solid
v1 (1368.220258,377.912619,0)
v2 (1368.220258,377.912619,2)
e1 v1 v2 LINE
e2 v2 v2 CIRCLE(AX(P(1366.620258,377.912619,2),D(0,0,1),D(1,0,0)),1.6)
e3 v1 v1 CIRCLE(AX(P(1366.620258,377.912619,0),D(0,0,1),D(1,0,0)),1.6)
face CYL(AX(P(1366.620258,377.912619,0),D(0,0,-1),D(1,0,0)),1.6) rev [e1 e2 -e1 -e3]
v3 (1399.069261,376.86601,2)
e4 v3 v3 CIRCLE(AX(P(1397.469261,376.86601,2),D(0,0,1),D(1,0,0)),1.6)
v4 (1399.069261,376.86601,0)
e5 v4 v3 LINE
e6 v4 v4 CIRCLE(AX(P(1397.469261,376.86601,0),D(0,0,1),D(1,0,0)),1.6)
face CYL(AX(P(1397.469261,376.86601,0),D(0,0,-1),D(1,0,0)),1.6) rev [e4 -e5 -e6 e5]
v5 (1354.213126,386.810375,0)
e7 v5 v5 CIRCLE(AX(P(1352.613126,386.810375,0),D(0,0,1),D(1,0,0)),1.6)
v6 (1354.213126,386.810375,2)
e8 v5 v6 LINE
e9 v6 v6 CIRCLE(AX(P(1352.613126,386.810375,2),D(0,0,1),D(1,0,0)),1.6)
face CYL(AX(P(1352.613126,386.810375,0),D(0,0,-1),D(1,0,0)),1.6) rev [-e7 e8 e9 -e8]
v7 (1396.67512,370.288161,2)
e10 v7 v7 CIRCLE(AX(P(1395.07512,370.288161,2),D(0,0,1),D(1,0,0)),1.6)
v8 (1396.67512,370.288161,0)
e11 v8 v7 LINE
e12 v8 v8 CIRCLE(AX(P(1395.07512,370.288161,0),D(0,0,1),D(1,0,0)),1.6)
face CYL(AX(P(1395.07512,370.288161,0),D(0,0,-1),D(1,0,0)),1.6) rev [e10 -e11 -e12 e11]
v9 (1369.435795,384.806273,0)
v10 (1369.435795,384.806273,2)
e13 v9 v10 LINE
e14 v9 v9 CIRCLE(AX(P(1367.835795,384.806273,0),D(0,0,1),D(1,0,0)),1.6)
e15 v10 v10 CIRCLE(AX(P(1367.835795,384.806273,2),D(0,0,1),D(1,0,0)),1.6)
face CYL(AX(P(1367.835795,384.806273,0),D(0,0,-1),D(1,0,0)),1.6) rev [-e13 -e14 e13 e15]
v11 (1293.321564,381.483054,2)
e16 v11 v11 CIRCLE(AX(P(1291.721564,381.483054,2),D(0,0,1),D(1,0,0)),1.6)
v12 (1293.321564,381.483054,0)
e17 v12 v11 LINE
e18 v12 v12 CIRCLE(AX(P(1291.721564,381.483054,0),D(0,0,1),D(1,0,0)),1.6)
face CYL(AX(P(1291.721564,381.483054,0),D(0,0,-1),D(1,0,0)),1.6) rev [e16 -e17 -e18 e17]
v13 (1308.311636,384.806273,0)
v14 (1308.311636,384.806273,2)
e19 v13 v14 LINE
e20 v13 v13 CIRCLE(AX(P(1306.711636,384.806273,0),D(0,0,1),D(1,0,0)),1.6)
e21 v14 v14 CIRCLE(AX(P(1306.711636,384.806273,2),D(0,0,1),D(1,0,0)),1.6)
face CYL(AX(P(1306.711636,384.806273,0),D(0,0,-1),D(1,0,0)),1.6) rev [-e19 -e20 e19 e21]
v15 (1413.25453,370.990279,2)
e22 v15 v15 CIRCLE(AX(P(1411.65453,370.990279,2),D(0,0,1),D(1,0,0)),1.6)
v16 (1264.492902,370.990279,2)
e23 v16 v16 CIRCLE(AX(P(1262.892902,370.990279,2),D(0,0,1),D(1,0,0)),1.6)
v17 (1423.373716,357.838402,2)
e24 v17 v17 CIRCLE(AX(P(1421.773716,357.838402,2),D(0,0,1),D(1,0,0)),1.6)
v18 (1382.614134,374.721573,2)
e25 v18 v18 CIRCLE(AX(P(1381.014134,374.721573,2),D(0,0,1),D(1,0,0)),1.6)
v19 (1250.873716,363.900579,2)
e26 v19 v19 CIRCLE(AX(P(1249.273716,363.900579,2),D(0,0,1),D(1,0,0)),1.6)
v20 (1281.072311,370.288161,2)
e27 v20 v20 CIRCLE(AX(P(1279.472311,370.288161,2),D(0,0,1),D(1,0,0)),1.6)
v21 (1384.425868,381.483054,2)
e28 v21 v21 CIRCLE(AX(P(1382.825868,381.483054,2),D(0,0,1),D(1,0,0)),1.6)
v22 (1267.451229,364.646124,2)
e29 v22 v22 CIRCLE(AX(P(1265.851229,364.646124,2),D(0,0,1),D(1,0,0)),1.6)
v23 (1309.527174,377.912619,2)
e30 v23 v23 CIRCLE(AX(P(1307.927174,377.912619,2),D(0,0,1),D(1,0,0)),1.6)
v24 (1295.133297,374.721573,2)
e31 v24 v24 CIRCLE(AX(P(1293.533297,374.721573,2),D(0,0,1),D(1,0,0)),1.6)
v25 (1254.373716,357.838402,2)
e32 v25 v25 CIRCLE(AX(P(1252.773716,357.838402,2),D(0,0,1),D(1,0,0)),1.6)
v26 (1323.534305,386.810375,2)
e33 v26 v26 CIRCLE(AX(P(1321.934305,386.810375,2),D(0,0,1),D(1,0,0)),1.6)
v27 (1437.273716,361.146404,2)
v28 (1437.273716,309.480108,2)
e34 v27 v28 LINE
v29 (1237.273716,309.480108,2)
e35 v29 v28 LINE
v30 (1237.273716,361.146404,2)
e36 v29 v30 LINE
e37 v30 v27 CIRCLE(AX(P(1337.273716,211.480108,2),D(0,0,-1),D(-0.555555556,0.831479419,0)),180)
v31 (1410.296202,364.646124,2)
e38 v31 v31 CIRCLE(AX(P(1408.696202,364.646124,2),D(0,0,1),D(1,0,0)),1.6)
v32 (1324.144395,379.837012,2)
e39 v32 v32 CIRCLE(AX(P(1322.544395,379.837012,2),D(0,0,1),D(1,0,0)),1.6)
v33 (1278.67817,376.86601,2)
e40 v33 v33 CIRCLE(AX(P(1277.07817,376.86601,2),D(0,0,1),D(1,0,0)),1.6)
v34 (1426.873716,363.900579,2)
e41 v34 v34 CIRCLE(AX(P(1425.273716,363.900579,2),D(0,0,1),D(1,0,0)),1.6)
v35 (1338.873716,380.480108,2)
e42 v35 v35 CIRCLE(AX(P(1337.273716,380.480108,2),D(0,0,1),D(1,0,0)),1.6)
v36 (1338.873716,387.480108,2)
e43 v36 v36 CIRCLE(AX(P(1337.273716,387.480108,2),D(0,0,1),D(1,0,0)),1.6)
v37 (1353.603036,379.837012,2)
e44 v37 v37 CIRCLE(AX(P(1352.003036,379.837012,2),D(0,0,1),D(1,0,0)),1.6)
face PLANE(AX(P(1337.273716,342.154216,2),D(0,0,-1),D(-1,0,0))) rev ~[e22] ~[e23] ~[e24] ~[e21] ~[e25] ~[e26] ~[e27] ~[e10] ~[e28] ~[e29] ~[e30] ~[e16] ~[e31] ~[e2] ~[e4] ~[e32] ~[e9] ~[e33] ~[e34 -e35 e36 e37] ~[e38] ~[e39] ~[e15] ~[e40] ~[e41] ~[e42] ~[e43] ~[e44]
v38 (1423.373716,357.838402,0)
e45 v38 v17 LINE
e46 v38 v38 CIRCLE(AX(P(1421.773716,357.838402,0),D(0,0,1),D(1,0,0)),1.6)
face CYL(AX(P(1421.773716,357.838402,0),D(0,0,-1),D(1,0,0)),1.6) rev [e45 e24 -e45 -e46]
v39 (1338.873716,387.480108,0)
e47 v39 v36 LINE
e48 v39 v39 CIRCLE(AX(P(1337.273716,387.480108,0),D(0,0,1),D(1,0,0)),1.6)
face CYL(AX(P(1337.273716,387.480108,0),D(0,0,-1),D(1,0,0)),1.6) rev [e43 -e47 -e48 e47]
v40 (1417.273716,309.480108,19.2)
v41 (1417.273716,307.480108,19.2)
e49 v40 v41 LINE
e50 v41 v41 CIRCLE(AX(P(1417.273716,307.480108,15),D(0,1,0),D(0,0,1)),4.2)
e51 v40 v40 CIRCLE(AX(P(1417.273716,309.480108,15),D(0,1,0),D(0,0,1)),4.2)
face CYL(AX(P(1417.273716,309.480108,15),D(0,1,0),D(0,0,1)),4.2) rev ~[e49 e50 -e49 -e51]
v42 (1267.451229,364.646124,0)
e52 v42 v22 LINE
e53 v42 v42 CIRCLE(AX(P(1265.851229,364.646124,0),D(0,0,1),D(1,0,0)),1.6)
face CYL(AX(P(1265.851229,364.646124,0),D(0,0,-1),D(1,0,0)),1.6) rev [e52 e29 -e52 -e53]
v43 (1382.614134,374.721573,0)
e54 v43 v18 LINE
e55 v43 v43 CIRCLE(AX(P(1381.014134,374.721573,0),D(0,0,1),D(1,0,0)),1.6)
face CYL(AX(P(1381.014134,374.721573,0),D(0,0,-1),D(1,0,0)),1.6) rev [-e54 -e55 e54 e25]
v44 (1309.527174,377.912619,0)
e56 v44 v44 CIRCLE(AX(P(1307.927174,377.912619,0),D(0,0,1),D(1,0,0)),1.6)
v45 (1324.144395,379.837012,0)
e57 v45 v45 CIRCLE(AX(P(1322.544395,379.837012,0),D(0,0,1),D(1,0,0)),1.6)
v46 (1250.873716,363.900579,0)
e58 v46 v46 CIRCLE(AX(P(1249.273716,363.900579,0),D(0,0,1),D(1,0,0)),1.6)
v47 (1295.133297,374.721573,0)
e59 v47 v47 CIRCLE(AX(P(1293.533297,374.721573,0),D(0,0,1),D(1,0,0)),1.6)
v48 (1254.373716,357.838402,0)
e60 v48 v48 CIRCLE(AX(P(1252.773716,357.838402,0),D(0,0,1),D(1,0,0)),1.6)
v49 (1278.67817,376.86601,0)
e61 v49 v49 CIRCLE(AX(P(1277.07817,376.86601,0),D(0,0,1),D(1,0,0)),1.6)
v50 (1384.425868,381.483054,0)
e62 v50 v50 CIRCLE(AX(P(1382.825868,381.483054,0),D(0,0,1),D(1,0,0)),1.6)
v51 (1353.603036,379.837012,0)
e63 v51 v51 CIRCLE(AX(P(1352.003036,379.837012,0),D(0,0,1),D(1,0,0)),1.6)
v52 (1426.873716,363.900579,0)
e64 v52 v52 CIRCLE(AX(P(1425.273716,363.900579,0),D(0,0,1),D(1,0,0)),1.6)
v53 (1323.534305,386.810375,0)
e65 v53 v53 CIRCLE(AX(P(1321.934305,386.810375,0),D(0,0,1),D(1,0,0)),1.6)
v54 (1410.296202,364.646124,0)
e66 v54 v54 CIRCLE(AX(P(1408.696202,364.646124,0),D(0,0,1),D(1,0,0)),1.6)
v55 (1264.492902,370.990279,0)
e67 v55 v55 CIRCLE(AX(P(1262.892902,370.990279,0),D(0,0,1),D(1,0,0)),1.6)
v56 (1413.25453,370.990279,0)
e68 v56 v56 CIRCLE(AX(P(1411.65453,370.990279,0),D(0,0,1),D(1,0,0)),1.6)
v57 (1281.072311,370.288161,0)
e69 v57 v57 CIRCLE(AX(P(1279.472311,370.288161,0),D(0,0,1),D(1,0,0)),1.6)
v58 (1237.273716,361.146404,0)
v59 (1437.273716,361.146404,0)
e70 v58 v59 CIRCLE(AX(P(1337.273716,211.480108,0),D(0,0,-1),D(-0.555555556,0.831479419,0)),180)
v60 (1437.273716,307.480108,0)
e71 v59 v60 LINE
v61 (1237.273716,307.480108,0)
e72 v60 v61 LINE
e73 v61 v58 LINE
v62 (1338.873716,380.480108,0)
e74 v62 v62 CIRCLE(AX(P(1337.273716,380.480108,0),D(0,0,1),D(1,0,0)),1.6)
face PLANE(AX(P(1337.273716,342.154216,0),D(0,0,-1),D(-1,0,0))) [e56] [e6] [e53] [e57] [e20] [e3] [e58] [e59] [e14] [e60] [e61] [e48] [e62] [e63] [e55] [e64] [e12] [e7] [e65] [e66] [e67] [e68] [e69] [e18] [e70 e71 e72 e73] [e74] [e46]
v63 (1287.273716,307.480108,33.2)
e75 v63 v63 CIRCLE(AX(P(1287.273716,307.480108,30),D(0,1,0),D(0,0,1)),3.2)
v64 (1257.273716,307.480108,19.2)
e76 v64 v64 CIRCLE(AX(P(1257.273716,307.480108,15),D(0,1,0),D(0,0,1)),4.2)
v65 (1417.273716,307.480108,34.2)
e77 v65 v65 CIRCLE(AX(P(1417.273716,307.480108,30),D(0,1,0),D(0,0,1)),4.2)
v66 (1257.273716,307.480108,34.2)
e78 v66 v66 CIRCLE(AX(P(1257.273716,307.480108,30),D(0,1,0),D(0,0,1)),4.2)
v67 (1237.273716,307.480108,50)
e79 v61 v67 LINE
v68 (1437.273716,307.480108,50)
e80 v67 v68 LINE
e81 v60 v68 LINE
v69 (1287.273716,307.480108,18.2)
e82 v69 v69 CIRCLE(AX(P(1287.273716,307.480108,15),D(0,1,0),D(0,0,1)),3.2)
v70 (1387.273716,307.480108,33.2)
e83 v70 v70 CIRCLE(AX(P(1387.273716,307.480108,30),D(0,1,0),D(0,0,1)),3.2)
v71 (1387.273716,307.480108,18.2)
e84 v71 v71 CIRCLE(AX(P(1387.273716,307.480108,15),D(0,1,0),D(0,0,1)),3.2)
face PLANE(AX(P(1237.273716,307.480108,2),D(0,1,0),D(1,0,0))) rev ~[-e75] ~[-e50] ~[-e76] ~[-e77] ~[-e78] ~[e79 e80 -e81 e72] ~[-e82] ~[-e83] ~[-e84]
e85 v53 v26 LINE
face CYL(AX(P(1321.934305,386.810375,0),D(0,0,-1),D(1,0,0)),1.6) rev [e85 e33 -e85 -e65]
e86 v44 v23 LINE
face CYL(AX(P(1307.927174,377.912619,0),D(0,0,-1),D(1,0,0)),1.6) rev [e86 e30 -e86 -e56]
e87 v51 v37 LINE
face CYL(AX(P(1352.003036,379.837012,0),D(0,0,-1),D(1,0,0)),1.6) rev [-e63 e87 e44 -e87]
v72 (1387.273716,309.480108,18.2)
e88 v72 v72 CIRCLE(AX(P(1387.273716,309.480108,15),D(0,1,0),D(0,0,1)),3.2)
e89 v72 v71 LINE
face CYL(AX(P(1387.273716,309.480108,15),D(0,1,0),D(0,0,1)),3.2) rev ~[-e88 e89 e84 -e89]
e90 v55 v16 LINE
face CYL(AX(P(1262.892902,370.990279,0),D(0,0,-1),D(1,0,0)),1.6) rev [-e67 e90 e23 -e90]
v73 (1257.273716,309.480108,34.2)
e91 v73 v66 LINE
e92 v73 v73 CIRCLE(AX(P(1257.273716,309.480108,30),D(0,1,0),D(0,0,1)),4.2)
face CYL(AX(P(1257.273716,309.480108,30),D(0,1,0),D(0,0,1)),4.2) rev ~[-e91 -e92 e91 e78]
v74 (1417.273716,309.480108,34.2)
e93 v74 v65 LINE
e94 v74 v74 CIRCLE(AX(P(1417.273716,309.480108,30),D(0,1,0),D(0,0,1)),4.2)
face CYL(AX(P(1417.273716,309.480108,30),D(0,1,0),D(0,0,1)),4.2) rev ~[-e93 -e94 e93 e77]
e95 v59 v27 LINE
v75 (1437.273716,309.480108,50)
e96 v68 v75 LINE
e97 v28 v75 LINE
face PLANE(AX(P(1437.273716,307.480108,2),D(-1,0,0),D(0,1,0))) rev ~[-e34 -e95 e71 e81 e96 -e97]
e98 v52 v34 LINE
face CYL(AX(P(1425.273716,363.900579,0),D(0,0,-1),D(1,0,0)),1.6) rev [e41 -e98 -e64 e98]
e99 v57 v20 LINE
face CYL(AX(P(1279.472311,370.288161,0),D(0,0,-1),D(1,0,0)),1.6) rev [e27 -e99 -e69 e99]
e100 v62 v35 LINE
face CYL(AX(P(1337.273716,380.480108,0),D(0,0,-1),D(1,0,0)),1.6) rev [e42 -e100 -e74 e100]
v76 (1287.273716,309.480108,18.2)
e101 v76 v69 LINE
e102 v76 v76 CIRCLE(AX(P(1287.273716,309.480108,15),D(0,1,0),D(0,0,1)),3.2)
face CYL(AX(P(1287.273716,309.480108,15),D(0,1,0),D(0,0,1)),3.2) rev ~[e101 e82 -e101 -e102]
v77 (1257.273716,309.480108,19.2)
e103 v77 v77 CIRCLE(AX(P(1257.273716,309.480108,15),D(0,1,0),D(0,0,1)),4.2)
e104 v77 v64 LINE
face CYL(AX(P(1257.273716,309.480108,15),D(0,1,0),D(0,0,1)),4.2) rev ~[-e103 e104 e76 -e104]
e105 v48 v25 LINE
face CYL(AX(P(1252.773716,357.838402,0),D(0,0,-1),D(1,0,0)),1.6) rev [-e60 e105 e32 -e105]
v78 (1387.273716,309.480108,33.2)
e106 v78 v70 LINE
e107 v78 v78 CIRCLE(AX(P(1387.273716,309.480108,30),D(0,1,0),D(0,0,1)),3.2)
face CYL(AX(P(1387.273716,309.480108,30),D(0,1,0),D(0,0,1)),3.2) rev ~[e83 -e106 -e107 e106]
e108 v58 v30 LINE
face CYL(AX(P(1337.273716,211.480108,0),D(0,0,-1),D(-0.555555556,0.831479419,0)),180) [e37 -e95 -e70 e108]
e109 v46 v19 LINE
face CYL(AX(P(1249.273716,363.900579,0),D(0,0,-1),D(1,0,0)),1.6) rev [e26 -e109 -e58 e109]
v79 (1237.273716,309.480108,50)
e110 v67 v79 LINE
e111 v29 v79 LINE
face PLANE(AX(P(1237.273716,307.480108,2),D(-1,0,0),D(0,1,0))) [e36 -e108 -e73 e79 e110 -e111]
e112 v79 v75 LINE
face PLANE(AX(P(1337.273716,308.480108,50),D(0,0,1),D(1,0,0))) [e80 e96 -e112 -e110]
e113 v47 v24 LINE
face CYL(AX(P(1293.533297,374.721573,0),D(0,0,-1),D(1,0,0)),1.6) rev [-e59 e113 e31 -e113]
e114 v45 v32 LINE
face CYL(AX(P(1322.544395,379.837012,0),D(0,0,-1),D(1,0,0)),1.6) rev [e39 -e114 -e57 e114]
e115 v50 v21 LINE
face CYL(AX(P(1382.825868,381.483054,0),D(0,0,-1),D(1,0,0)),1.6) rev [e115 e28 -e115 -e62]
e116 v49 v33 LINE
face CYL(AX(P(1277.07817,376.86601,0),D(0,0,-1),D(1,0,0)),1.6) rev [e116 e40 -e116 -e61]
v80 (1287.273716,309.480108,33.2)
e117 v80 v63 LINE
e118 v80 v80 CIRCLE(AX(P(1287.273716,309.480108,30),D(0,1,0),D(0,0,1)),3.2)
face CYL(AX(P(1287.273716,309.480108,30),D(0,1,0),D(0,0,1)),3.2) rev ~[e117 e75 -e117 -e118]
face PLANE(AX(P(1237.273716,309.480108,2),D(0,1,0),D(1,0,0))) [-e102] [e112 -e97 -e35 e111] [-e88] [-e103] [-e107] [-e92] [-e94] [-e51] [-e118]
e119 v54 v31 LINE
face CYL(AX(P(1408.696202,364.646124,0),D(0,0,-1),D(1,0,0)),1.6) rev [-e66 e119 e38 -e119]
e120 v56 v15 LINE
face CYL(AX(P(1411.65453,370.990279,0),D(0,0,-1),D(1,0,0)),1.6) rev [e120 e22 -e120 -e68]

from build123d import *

# Parameters (mm, degrees)
SKETCH_1_R          = 1.6
EXTRUDE_1_DEPTH     = 2
SKETCH_2_W          = 200
SKETCH_2_H          = 2
EXTRUDE_2_DEPTH     = 48
SKETCH_3_R          = 3.2
SKETCH_3_R_2        = 4.2
CUT_EXTRUDE_1_DEPTH = 48


with BuildPart() as part:
    # 草图1 → 凸台-拉伸1 (new body)
    with BuildSketch(Plane.XY):
        with BuildLine():
            Line((1437.273715593, 307.480108419), (1237.273715593, 307.480108419))
            Line((1237.273715593, 307.480108419), (1237.273715593, 361.14640389))
            ThreePointArc((1237.273715593, 361.14640389), (1337.273715593, 391.480108419), (1437.273715593, 361.14640389))
            Line((1437.273715593, 361.14640389), (1437.273715593, 307.480108419))
        make_face()
        with Locations((1337.273715593, 387.480108419)):
            Circle(SKETCH_1_R, mode=Mode.SUBTRACT)
        with Locations((1337.273715593, 380.480108419)):
            Circle(SKETCH_1_R, mode=Mode.SUBTRACT)
        with Locations((1321.934304869, 386.810375283)):
            Circle(SKETCH_1_R, mode=Mode.SUBTRACT)
        with Locations((1322.544395068, 379.837012397)):
            Circle(SKETCH_1_R, mode=Mode.SUBTRACT)
        with Locations((1306.711636323, 384.806272949)):
            Circle(SKETCH_1_R, mode=Mode.SUBTRACT)
        with Locations((1307.927173567, 377.912618678)):
            Circle(SKETCH_1_R, mode=Mode.SUBTRACT)
        with Locations((1291.721563655, 381.483053846)):
            Circle(SKETCH_1_R, mode=Mode.SUBTRACT)
        with Locations((1293.53329697, 374.721573062)):
            Circle(SKETCH_1_R, mode=Mode.SUBTRACT)
        with Locations((1277.078170367, 376.866009678)):
            Circle(SKETCH_1_R, mode=Mode.SUBTRACT)
        with Locations((1279.472311371, 370.288161332)):
            Circle(SKETCH_1_R, mode=Mode.SUBTRACT)
        with Locations((1262.892901526, 370.990278938)):
            Circle(SKETCH_1_R, mode=Mode.SUBTRACT)
        with Locations((1265.851229359, 364.646124428)):
            Circle(SKETCH_1_R, mode=Mode.SUBTRACT)
        with Locations((1249.273715593, 363.900579485)):
            Circle(SKETCH_1_R, mode=Mode.SUBTRACT)
        with Locations((1252.773715593, 357.838401659)):
            Circle(SKETCH_1_R, mode=Mode.SUBTRACT)
        with Locations((1425.273715593, 363.900579485)):
            Circle(SKETCH_1_R, mode=Mode.SUBTRACT)
        with Locations((1421.773715593, 357.838401659)):
            Circle(SKETCH_1_R, mode=Mode.SUBTRACT)
        with Locations((1411.654529659, 370.990278938)):
            Circle(SKETCH_1_R, mode=Mode.SUBTRACT)
        with Locations((1408.696201827, 364.646124428)):
            Circle(SKETCH_1_R, mode=Mode.SUBTRACT)
        with Locations((1397.469260818, 376.866009678)):
            Circle(SKETCH_1_R, mode=Mode.SUBTRACT)
        with Locations((1395.075119815, 370.288161332)):
            Circle(SKETCH_1_R, mode=Mode.SUBTRACT)
        with Locations((1382.825867531, 381.483053846)):
            Circle(SKETCH_1_R, mode=Mode.SUBTRACT)
        with Locations((1381.014134215, 374.721573062)):
            Circle(SKETCH_1_R, mode=Mode.SUBTRACT)
        with Locations((1367.835794862, 384.806272949)):
            Circle(SKETCH_1_R, mode=Mode.SUBTRACT)
        with Locations((1366.620257618, 377.912618678)):
            Circle(SKETCH_1_R, mode=Mode.SUBTRACT)
        with Locations((1352.613126316, 386.810375283)):
            Circle(SKETCH_1_R, mode=Mode.SUBTRACT)
        with Locations((1352.003036117, 379.837012397)):
            Circle(SKETCH_1_R, mode=Mode.SUBTRACT)
    extrude(amount=EXTRUDE_1_DEPTH)

    # 草图2 → 凸台-拉伸2 (add)
    with BuildSketch(Plane.XY.offset(2)):
        with Locations((1337.273715593, 308.480108419)):
            Rectangle(SKETCH_2_W, SKETCH_2_H)
    extrude(amount=EXTRUDE_2_DEPTH)

    # 草图3 → 切除-拉伸1 (cut)
    with BuildSketch(Plane(origin=(0, 309.480108419, 0), x_dir=(1, 0, 0), z_dir=(0, 1, 0))):
        with Locations(Location((1287.273715593, -30, 0), (0, 0, 270))):
            Circle(SKETCH_3_R)
        with Locations(Location((1387.273715593, -30, 0), (0, 0, 270))):
            Circle(SKETCH_3_R)
        with Locations(Location((1257.273715593, -15, 0), (0, 0, 270))):
            Circle(SKETCH_3_R_2)
        with Locations(Location((1417.273715593, -15, 0), (0, 0, 270))):
            Circle(SKETCH_3_R_2)
        with Locations(Location((1257.273715593, -30, 0), (0, 0, 270))):
            Circle(SKETCH_3_R_2)
        with Locations(Location((1287.273715593, -15, 0), (0, 0, 270))):
            Circle(SKETCH_3_R)
        with Locations(Location((1387.273715593, -15, 0), (0, 0, 270))):
            Circle(SKETCH_3_R)
        with Locations(Location((1417.273715593, -30, 0), (0, 0, 270))):
            Circle(SKETCH_3_R_2)
    extrude(amount=-CUT_EXTRUDE_1_DEPTH, mode=Mode.SUBTRACT)


solid = part.part
